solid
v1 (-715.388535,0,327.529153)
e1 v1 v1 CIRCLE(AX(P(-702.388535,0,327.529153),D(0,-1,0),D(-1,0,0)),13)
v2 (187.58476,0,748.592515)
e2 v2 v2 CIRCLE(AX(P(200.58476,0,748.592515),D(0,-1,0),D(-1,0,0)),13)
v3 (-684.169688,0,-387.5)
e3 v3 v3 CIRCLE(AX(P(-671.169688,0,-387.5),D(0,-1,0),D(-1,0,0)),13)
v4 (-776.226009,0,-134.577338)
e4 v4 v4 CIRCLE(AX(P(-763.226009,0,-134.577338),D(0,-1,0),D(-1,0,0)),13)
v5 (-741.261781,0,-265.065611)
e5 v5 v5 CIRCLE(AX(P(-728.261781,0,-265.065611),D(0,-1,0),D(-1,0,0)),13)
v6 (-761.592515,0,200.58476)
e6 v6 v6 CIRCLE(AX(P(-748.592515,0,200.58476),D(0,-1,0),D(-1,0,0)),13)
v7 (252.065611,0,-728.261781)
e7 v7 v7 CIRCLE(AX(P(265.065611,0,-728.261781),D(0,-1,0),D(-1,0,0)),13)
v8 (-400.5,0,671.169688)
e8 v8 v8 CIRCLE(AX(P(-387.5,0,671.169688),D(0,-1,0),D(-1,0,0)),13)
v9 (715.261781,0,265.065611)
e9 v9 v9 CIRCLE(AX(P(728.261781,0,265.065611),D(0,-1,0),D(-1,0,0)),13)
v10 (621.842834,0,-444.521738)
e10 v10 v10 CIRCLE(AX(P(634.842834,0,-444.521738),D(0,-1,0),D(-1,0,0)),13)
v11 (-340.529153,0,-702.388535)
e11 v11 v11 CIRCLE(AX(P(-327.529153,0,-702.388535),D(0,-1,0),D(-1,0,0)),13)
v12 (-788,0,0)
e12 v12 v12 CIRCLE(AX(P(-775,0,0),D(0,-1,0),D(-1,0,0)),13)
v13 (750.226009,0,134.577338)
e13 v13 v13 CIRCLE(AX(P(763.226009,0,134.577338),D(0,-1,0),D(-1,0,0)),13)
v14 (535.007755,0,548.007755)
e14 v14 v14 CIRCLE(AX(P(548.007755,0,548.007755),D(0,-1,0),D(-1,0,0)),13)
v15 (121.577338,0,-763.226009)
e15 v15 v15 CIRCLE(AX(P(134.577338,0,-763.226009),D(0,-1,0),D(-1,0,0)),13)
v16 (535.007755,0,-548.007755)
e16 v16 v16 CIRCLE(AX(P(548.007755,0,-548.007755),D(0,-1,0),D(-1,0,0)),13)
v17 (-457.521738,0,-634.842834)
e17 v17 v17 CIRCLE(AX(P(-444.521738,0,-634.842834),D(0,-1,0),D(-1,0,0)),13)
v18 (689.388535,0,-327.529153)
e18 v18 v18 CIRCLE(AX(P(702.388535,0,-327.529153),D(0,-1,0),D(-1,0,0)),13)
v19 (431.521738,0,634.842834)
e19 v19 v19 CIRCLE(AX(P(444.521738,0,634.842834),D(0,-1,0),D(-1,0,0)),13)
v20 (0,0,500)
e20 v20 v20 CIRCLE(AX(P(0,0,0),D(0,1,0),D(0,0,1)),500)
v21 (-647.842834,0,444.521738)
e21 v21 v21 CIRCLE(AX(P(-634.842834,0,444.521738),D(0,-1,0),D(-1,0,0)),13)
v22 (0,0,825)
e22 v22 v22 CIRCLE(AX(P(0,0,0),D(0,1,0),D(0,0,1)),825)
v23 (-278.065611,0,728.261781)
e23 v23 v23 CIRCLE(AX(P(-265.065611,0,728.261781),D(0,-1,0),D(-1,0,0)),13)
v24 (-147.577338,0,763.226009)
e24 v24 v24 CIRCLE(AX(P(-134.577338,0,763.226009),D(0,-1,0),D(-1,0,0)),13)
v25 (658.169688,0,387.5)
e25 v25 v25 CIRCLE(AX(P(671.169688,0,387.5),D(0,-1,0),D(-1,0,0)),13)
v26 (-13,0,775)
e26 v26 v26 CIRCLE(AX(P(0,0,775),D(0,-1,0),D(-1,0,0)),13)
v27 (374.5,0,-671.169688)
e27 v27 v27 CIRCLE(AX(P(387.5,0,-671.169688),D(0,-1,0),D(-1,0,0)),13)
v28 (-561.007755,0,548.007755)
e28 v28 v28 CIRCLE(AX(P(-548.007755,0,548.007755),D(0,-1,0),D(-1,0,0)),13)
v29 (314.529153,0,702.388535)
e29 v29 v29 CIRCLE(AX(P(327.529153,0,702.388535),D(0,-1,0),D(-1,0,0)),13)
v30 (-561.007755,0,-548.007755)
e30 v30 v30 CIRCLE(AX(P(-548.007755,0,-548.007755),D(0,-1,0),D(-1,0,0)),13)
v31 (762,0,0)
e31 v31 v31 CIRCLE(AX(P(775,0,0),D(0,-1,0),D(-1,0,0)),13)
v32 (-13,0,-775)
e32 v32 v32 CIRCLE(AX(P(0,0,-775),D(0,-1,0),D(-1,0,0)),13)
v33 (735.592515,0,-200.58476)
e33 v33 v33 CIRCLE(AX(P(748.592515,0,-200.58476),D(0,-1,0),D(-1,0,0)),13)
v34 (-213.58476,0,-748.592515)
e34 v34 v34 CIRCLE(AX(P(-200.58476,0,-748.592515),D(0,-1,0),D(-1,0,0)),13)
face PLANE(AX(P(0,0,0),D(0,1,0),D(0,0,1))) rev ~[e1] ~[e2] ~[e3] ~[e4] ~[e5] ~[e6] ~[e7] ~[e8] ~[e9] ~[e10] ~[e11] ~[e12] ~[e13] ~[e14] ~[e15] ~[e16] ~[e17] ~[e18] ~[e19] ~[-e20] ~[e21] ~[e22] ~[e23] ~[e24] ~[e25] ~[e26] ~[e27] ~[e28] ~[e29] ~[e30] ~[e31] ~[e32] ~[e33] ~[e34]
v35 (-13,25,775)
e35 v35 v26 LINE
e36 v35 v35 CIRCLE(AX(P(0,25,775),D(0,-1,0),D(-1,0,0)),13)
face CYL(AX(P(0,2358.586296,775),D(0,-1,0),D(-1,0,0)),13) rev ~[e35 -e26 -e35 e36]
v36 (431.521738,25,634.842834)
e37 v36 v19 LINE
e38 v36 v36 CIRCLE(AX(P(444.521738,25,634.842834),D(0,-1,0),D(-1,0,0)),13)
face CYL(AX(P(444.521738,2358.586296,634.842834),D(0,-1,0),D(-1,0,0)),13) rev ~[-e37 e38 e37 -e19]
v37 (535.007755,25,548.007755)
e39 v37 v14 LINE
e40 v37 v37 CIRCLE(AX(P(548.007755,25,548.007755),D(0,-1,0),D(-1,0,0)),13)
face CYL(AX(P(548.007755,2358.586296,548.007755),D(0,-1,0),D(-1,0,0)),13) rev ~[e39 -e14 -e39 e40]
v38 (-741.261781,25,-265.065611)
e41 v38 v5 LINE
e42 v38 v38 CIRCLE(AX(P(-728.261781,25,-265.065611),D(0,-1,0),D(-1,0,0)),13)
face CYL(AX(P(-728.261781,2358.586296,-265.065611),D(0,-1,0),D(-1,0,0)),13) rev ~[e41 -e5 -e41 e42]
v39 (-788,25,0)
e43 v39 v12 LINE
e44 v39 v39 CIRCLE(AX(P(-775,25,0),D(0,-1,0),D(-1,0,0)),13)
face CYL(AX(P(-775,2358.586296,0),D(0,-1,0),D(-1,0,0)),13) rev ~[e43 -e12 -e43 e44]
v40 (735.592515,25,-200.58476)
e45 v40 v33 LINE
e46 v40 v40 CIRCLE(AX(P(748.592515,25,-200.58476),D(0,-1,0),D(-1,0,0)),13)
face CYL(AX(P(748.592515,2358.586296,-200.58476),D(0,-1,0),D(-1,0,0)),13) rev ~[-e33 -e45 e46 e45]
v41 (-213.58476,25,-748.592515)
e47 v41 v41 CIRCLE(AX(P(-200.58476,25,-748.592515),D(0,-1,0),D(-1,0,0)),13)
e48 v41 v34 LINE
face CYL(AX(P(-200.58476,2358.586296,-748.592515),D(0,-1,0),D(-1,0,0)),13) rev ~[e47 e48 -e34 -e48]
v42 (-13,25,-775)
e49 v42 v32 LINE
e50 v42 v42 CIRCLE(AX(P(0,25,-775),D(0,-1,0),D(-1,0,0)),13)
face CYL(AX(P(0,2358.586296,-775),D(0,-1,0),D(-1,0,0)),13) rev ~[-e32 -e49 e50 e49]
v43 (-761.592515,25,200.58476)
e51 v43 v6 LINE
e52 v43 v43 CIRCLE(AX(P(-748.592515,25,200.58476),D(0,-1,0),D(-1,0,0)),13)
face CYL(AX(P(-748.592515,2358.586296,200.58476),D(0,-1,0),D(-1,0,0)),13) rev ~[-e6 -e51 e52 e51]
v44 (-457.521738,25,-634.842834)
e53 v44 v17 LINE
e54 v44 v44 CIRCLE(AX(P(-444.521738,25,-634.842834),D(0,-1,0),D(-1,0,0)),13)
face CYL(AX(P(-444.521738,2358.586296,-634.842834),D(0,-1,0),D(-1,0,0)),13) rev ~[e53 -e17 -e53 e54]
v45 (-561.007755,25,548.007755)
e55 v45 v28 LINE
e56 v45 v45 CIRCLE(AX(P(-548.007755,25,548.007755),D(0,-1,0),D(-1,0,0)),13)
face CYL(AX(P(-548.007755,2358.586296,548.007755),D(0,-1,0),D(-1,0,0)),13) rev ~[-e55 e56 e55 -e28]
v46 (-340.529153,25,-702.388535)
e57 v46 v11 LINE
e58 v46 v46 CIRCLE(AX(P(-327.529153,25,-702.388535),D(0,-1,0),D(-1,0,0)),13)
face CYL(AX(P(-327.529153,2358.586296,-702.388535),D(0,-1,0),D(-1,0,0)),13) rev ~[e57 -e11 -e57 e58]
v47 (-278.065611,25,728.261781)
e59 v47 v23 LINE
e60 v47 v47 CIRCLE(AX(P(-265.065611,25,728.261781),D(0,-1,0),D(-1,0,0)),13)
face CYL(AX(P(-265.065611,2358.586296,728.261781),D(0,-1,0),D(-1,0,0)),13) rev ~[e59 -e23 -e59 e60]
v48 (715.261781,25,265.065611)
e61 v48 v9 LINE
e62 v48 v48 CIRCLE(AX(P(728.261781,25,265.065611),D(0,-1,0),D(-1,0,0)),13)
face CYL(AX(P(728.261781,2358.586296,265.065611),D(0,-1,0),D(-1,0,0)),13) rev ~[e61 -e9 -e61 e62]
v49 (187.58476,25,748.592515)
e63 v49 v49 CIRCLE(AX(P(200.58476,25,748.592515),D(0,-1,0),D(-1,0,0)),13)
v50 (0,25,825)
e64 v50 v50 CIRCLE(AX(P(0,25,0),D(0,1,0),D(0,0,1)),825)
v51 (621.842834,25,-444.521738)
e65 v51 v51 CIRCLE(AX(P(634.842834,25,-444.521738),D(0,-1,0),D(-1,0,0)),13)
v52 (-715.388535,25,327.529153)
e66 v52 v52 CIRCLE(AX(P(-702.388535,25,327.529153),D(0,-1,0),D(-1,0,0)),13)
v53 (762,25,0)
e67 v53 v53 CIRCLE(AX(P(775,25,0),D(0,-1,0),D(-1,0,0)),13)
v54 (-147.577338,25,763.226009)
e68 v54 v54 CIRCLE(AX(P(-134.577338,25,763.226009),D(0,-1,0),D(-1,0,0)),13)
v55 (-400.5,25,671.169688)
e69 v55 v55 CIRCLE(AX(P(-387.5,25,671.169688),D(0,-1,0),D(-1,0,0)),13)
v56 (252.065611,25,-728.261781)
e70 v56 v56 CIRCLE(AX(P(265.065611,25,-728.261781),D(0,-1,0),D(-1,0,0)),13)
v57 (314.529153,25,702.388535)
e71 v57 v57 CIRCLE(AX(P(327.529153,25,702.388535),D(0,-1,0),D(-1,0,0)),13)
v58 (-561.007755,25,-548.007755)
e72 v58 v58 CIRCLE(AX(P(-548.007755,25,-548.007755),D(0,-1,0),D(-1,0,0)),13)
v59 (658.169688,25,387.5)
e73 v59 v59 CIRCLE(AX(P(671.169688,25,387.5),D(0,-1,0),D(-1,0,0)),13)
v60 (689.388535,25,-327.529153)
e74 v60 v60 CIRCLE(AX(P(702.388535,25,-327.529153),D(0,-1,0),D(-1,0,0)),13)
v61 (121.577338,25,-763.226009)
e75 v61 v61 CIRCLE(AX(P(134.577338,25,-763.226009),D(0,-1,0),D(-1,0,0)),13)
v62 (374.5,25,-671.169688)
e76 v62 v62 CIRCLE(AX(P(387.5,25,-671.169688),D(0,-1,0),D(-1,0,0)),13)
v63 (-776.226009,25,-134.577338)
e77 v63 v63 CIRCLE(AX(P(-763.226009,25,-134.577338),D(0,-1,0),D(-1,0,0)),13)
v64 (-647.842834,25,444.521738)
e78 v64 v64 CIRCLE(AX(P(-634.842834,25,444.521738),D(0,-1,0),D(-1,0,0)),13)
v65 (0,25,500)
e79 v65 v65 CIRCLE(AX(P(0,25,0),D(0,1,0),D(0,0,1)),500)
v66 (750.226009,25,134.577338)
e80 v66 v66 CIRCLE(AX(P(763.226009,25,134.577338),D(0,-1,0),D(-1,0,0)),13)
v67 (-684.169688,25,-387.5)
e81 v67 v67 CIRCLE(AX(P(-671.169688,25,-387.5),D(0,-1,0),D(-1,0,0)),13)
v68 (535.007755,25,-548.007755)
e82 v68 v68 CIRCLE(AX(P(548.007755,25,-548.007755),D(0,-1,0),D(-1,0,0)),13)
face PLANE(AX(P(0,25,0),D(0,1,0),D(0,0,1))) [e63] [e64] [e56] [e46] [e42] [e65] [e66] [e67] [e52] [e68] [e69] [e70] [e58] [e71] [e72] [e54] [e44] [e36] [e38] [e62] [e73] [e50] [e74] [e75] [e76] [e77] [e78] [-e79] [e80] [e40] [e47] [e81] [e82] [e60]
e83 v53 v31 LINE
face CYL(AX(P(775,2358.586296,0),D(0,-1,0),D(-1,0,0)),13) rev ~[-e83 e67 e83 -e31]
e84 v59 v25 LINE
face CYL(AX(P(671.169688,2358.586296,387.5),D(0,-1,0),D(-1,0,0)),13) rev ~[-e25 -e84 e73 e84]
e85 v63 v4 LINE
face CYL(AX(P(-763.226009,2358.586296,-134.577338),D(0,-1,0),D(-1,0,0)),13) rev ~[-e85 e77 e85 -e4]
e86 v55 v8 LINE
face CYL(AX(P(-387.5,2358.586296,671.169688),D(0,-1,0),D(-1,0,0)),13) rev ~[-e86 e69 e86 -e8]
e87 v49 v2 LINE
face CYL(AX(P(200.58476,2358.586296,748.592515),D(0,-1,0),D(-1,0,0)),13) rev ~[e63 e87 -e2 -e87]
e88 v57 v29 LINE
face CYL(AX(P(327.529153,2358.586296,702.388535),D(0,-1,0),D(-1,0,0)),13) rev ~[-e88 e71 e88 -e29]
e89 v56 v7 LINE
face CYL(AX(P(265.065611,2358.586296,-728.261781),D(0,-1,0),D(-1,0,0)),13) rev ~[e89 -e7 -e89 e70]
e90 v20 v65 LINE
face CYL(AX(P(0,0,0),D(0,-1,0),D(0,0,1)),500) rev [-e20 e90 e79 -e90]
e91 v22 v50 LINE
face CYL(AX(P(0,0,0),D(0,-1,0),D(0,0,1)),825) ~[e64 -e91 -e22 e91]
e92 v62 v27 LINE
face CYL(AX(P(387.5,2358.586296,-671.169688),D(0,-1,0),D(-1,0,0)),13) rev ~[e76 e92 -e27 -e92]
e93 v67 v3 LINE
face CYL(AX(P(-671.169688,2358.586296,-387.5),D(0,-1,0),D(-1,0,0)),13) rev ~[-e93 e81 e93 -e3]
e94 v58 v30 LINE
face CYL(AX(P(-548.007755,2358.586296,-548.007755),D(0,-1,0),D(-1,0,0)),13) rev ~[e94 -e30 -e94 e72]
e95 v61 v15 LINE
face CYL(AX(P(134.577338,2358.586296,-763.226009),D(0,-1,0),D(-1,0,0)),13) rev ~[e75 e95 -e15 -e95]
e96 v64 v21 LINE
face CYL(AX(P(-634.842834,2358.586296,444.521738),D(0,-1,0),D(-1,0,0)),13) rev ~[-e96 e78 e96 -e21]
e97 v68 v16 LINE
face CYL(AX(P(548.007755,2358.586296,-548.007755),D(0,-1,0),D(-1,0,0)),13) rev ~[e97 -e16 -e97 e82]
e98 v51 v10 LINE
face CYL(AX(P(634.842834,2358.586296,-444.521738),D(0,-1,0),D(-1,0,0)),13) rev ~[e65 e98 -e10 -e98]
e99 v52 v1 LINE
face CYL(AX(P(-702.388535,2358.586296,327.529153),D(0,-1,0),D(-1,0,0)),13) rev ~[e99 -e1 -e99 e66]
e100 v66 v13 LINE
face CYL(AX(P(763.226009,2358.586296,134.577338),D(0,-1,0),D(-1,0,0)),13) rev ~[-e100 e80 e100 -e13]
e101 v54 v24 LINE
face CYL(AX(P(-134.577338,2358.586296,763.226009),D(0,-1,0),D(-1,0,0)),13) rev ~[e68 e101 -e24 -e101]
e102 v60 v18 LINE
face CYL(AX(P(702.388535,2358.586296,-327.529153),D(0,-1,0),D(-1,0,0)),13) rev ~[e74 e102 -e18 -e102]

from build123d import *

# Parameters (mm, degrees)
SKETCH1_R                    = 825
SKETCH1_R_2                  = 500
BOSS_EXTRUDE1_DEPTH          = 25
F_24_5_24_5_DIAMETER_HOLE1_D = 26


with BuildPart() as part:
    # Sketch1 → Boss-Extrude1 (new body)
    with BuildSketch(Plane(origin=(0, 0, 0), x_dir=(1, 0, 0), z_dir=(0, 1, 0))):
        with Locations(Location((0, 0, 0), (0, 0, 270))):
            Circle(SKETCH1_R)
        with Locations(Location((0, 0, 0), (0, 0, 270))):
            Circle(SKETCH1_R_2, mode=Mode.SUBTRACT)
    extrude(amount=BOSS_EXTRUDE1_DEPTH)

    # Ø24.5 (24.5) Diameter Hole1 (through all)
    with Locations(Plane(origin=(0, 25, 0), x_dir=(1, 0, 0), z_dir=(0, 1, 0))):
        with Locations((0, 775), (134.577337692, 763.226008584), (265.065611077, 728.261781109), (387.5, 671.169687933), (548.00775542, 548.00775542), (634.842834324, 444.521738172), (702.388534953, 327.529152849), (748.592515374, 200.584759954), (775, 0), (763.226008584, -134.577337692), (728.261781109, -265.065611077), (671.169687933, -387.5), (548.00775542, -548.00775542), (444.521738172, -634.842834324), (327.529152849, -702.388534953), (200.584759954, -748.592515374), (0, -775), (-134.577337692, -763.226008584), (-265.065611077, -728.261781109), (-387.5, -671.169687933), (-548.00775542, -548.00775542), (-634.842834324, -444.521738172), (-702.388534953, -327.529152849), (-748.592515374, -200.584759954), (-775, 0), (-763.226008584, 134.577337692), (-728.261781109, 265.065611077), (-671.169687933, 387.5), (-548.00775542, 548.00775542), (-444.521738172, 634.842834324), (-327.529152849, 702.388534953), (-200.584759954, 748.592515374)):
            Hole(F_24_5_24_5_DIAMETER_HOLE1_D / 2)


solid = part.part
